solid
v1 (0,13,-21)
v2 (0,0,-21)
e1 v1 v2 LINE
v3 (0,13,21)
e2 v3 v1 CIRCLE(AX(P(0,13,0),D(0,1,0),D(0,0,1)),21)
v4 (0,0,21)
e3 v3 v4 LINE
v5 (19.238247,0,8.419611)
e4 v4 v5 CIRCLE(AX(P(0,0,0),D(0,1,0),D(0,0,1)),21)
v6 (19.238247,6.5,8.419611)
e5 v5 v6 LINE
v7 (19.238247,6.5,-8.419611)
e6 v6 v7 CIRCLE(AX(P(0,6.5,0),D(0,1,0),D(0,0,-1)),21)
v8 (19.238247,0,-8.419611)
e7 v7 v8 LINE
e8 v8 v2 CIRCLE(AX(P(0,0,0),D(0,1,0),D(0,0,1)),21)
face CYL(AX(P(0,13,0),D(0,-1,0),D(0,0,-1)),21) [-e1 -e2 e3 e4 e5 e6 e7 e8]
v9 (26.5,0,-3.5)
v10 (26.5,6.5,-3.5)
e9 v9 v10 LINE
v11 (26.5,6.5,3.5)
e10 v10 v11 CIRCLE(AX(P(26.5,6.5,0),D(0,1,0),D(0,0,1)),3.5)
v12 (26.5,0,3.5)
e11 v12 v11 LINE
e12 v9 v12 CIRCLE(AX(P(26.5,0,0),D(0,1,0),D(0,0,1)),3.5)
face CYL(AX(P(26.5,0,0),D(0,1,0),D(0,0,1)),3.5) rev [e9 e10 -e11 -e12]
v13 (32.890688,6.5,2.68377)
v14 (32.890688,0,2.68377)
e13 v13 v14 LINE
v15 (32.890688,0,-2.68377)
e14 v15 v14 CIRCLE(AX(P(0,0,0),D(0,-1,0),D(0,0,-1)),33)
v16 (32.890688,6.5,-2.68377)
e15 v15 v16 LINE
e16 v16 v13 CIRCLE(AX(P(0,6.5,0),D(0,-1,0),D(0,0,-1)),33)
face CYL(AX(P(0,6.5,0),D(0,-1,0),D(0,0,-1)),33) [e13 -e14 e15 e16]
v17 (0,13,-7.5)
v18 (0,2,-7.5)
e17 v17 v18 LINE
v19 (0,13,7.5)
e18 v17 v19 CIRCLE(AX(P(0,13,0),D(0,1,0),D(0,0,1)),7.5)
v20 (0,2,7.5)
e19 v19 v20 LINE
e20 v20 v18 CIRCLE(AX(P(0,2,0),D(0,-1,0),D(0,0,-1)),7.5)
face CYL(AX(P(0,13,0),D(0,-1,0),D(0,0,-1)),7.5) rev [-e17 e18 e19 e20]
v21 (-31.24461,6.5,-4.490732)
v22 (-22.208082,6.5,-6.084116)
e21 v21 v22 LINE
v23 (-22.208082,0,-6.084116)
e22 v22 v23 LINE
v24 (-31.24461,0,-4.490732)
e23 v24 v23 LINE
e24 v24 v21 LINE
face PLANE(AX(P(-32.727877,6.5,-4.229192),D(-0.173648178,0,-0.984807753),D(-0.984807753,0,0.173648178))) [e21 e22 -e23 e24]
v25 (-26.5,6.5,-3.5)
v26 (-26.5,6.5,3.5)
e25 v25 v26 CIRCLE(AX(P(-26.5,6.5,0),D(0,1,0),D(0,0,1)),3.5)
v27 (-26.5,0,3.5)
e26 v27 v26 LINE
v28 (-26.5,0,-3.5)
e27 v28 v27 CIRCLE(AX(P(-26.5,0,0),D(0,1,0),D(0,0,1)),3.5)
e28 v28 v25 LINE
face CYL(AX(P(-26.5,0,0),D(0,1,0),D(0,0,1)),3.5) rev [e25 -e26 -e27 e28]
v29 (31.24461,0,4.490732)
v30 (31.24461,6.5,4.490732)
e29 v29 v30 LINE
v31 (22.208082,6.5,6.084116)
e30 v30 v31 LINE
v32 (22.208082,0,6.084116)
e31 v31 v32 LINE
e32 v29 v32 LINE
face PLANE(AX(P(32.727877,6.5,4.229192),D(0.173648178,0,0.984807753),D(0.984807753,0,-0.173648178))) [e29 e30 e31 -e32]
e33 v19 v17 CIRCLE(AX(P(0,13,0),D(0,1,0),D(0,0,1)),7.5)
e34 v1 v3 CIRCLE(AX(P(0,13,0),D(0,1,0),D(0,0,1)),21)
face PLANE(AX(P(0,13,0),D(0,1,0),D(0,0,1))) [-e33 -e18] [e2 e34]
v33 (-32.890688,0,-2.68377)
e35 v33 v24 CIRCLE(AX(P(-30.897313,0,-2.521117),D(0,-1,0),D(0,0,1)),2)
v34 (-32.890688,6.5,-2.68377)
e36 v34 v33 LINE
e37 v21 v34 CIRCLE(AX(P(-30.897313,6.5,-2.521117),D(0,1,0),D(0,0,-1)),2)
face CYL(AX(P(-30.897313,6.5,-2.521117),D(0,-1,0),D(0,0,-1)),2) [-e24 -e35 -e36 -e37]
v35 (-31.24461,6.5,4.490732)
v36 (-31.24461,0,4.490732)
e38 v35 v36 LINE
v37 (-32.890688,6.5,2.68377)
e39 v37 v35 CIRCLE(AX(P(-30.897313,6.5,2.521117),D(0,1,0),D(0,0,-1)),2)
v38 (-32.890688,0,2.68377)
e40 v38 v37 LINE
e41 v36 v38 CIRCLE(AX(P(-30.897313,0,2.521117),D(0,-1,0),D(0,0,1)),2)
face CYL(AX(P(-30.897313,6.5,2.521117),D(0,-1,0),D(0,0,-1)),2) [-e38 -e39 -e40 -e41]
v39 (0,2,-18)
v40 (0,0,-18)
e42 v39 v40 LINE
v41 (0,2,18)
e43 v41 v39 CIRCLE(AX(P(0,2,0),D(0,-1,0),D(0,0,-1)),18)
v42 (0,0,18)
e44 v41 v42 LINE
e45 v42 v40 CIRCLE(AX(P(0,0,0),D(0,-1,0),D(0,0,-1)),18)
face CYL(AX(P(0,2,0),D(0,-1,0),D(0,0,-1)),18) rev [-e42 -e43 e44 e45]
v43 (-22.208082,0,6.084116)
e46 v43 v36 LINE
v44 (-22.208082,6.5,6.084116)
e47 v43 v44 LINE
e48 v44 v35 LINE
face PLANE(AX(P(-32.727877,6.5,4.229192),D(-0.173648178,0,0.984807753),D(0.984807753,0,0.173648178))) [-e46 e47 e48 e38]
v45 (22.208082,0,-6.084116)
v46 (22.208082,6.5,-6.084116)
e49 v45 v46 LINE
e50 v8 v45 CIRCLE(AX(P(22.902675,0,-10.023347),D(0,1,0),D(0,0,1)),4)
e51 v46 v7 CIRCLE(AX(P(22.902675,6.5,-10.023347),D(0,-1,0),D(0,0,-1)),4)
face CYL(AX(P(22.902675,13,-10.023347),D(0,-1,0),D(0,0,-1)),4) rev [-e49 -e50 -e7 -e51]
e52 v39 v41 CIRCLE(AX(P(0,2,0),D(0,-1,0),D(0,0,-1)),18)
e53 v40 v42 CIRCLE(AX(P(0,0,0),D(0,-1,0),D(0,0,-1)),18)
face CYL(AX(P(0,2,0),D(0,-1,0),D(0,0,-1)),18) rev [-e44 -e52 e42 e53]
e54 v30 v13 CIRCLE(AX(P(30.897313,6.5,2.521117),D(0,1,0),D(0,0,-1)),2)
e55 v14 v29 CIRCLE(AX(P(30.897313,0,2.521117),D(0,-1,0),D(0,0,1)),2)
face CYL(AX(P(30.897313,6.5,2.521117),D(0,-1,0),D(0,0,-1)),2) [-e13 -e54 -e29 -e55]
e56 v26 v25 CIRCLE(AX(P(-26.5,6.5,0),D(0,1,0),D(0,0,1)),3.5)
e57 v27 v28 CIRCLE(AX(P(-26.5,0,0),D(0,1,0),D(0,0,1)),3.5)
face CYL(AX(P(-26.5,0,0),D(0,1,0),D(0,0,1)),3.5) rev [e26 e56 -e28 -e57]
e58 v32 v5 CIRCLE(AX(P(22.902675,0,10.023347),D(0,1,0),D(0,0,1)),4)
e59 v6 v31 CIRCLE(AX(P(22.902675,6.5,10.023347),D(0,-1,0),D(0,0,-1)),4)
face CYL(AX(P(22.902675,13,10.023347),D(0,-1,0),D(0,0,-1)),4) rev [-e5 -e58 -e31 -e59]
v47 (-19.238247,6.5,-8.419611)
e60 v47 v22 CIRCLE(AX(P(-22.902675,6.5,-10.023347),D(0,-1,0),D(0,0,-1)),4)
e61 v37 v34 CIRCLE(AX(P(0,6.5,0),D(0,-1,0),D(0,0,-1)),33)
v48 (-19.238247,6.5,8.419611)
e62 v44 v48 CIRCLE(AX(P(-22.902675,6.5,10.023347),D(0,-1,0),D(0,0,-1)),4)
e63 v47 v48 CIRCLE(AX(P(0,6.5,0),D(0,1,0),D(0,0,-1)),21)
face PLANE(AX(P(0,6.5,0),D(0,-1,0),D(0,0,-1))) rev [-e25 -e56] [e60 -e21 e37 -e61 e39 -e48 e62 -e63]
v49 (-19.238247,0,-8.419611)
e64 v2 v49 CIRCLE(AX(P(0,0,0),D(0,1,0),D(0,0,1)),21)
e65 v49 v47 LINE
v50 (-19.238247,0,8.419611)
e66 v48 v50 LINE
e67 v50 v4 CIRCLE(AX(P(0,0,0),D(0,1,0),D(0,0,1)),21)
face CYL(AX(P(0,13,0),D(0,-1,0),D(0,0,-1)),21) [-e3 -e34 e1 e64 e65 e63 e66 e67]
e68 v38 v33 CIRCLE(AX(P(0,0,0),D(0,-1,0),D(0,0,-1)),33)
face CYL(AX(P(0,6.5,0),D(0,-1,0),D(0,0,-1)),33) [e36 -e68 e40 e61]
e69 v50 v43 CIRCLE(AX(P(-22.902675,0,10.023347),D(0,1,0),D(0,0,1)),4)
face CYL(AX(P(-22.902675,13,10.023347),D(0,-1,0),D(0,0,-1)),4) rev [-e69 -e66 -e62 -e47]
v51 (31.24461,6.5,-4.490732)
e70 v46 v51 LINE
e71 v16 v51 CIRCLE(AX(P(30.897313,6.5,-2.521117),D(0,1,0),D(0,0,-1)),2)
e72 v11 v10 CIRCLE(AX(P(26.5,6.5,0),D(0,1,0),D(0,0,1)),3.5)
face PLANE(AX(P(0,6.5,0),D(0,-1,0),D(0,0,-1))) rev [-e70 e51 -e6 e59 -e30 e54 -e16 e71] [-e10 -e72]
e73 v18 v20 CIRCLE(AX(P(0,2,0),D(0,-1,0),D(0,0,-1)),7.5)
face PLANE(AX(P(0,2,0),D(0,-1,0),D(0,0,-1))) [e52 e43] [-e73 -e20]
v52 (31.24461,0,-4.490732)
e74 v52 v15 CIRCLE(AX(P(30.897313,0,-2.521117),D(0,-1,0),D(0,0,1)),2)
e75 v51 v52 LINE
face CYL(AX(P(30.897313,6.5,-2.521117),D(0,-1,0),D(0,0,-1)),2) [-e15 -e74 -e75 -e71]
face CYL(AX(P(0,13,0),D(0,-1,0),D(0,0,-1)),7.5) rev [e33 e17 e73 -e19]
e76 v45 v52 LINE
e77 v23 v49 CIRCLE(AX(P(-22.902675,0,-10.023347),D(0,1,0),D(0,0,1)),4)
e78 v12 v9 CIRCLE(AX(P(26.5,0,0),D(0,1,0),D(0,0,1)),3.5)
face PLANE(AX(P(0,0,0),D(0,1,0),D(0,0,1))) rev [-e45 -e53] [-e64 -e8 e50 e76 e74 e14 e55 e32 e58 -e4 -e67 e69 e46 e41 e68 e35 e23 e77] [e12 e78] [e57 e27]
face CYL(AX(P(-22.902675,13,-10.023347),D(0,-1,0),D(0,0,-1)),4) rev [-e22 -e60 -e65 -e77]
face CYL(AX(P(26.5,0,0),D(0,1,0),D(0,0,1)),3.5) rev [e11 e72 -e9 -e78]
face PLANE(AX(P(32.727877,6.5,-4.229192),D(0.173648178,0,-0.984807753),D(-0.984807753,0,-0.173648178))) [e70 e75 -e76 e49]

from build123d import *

# Parameters (mm, degrees)
SKETCH_1_R          = 21
SKETCH_1_R_2        = 7.5
EXTRUDE_1_DEPTH     = 13
EXTRUDE_2_DEPTH     = 6.5
FILLET_1_R          = 4
FILLET_2_R          = 2
SKETCH_3_R          = 3.5
CUT_EXTRUDE_1_DEPTH = 6.5
SKETCH_4_R          = 18
CUT_EXTRUDE_2_DEPTH = 2


with BuildPart() as part:
    # 草图1 → 凸台-拉伸1 (new body)
    with BuildSketch(Plane(origin=(0, 0, 0), x_dir=(1, 0, 0), z_dir=(0, 1, 0))):
        with Locations(Location((0, 0, 0), (0, 0, 90))):
            Circle(SKETCH_1_R)
        with Locations(Location((0, 0, 0), (0, 0, 90))):
            Circle(SKETCH_1_R_2, mode=Mode.SUBTRACT)
    extrude(amount=EXTRUDE_1_DEPTH)

    # 草图2 → 凸台-拉伸2 (add)
    with BuildSketch(Plane.XZ):
        with BuildLine():
            Line((32.727876998, 4.229192264), (19.975971523, 6.477697255))
            ThreePointArc((19.975971523, 6.477697255), (21, 0), (19.975971523, -6.477697255))
            Line((19.975971523, -6.477697255), (32.727876998, -4.229192264))
            ThreePointArc((32.727876998, -4.229192264), (33, 0), (32.727876998, 4.229192264))
        make_face()
        with BuildLine():
            Line((-32.727876998, -4.229192264), (-19.975971523, -6.477697255))
            ThreePointArc((-19.975971523, -6.477697255), (-21, 0), (-19.975971523, 6.477697255))
            Line((-19.975971523, 6.477697255), (-32.727876998, 4.229192264))
            ThreePointArc((-32.727876998, 4.229192264), (-33, 0), (-32.727876998, -4.229192264))
        make_face()
    extrude(amount=-EXTRUDE_2_DEPTH)

    # 圆角1
    fillet_1_edges = [part.edges().sort_by_distance(p)[0] for p in [
        (19.975971523, 3.25, -6.477697255),
        (19.975971523, 3.25, 6.477697255),
        (-19.975971523, 3.25, 6.477697255),
        (-19.975971523, 3.25, -6.477697255),
    ]]
    fillet(fillet_1_edges, radius=FILLET_1_R)

    # 圆角2
    fillet_2_edges = [part.edges().sort_by_distance(p)[0] for p in [
        (32.727876998, 3.25, 4.229192264),
        (32.727876998, 3.25, -4.229192264),
        (-32.727876998, 3.25, -4.229192264),
        (-32.727876998, 3.25, 4.229192264),
    ]]
    fillet(fillet_2_edges, radius=FILLET_2_R)

    # 草图3 → 切除-拉伸1 (cut)
    with BuildSketch(Plane(origin=(0, 6.5, 0), x_dir=(1, 0, 0), z_dir=(0, 1, 0))):
        with Locations(Location((-26.5, 0, 0), (0, 0, 270))):
            Circle(SKETCH_3_R)
        with Locations(Location((26.5, 0, 0), (0, 0, 270))):
            Circle(SKETCH_3_R)
    extrude(amount=-CUT_EXTRUDE_1_DEPTH, mode=Mode.SUBTRACT)

    # 草图4 → 切除-拉伸2 (cut)
    with BuildSketch(Plane.XZ):
        with Locations(Location((0, 0, 0), (0, 0, 270))):
            Circle(SKETCH_4_R)
    extrude(amount=-CUT_EXTRUDE_2_DEPTH, mode=Mode.SUBTRACT)


solid = part.part
